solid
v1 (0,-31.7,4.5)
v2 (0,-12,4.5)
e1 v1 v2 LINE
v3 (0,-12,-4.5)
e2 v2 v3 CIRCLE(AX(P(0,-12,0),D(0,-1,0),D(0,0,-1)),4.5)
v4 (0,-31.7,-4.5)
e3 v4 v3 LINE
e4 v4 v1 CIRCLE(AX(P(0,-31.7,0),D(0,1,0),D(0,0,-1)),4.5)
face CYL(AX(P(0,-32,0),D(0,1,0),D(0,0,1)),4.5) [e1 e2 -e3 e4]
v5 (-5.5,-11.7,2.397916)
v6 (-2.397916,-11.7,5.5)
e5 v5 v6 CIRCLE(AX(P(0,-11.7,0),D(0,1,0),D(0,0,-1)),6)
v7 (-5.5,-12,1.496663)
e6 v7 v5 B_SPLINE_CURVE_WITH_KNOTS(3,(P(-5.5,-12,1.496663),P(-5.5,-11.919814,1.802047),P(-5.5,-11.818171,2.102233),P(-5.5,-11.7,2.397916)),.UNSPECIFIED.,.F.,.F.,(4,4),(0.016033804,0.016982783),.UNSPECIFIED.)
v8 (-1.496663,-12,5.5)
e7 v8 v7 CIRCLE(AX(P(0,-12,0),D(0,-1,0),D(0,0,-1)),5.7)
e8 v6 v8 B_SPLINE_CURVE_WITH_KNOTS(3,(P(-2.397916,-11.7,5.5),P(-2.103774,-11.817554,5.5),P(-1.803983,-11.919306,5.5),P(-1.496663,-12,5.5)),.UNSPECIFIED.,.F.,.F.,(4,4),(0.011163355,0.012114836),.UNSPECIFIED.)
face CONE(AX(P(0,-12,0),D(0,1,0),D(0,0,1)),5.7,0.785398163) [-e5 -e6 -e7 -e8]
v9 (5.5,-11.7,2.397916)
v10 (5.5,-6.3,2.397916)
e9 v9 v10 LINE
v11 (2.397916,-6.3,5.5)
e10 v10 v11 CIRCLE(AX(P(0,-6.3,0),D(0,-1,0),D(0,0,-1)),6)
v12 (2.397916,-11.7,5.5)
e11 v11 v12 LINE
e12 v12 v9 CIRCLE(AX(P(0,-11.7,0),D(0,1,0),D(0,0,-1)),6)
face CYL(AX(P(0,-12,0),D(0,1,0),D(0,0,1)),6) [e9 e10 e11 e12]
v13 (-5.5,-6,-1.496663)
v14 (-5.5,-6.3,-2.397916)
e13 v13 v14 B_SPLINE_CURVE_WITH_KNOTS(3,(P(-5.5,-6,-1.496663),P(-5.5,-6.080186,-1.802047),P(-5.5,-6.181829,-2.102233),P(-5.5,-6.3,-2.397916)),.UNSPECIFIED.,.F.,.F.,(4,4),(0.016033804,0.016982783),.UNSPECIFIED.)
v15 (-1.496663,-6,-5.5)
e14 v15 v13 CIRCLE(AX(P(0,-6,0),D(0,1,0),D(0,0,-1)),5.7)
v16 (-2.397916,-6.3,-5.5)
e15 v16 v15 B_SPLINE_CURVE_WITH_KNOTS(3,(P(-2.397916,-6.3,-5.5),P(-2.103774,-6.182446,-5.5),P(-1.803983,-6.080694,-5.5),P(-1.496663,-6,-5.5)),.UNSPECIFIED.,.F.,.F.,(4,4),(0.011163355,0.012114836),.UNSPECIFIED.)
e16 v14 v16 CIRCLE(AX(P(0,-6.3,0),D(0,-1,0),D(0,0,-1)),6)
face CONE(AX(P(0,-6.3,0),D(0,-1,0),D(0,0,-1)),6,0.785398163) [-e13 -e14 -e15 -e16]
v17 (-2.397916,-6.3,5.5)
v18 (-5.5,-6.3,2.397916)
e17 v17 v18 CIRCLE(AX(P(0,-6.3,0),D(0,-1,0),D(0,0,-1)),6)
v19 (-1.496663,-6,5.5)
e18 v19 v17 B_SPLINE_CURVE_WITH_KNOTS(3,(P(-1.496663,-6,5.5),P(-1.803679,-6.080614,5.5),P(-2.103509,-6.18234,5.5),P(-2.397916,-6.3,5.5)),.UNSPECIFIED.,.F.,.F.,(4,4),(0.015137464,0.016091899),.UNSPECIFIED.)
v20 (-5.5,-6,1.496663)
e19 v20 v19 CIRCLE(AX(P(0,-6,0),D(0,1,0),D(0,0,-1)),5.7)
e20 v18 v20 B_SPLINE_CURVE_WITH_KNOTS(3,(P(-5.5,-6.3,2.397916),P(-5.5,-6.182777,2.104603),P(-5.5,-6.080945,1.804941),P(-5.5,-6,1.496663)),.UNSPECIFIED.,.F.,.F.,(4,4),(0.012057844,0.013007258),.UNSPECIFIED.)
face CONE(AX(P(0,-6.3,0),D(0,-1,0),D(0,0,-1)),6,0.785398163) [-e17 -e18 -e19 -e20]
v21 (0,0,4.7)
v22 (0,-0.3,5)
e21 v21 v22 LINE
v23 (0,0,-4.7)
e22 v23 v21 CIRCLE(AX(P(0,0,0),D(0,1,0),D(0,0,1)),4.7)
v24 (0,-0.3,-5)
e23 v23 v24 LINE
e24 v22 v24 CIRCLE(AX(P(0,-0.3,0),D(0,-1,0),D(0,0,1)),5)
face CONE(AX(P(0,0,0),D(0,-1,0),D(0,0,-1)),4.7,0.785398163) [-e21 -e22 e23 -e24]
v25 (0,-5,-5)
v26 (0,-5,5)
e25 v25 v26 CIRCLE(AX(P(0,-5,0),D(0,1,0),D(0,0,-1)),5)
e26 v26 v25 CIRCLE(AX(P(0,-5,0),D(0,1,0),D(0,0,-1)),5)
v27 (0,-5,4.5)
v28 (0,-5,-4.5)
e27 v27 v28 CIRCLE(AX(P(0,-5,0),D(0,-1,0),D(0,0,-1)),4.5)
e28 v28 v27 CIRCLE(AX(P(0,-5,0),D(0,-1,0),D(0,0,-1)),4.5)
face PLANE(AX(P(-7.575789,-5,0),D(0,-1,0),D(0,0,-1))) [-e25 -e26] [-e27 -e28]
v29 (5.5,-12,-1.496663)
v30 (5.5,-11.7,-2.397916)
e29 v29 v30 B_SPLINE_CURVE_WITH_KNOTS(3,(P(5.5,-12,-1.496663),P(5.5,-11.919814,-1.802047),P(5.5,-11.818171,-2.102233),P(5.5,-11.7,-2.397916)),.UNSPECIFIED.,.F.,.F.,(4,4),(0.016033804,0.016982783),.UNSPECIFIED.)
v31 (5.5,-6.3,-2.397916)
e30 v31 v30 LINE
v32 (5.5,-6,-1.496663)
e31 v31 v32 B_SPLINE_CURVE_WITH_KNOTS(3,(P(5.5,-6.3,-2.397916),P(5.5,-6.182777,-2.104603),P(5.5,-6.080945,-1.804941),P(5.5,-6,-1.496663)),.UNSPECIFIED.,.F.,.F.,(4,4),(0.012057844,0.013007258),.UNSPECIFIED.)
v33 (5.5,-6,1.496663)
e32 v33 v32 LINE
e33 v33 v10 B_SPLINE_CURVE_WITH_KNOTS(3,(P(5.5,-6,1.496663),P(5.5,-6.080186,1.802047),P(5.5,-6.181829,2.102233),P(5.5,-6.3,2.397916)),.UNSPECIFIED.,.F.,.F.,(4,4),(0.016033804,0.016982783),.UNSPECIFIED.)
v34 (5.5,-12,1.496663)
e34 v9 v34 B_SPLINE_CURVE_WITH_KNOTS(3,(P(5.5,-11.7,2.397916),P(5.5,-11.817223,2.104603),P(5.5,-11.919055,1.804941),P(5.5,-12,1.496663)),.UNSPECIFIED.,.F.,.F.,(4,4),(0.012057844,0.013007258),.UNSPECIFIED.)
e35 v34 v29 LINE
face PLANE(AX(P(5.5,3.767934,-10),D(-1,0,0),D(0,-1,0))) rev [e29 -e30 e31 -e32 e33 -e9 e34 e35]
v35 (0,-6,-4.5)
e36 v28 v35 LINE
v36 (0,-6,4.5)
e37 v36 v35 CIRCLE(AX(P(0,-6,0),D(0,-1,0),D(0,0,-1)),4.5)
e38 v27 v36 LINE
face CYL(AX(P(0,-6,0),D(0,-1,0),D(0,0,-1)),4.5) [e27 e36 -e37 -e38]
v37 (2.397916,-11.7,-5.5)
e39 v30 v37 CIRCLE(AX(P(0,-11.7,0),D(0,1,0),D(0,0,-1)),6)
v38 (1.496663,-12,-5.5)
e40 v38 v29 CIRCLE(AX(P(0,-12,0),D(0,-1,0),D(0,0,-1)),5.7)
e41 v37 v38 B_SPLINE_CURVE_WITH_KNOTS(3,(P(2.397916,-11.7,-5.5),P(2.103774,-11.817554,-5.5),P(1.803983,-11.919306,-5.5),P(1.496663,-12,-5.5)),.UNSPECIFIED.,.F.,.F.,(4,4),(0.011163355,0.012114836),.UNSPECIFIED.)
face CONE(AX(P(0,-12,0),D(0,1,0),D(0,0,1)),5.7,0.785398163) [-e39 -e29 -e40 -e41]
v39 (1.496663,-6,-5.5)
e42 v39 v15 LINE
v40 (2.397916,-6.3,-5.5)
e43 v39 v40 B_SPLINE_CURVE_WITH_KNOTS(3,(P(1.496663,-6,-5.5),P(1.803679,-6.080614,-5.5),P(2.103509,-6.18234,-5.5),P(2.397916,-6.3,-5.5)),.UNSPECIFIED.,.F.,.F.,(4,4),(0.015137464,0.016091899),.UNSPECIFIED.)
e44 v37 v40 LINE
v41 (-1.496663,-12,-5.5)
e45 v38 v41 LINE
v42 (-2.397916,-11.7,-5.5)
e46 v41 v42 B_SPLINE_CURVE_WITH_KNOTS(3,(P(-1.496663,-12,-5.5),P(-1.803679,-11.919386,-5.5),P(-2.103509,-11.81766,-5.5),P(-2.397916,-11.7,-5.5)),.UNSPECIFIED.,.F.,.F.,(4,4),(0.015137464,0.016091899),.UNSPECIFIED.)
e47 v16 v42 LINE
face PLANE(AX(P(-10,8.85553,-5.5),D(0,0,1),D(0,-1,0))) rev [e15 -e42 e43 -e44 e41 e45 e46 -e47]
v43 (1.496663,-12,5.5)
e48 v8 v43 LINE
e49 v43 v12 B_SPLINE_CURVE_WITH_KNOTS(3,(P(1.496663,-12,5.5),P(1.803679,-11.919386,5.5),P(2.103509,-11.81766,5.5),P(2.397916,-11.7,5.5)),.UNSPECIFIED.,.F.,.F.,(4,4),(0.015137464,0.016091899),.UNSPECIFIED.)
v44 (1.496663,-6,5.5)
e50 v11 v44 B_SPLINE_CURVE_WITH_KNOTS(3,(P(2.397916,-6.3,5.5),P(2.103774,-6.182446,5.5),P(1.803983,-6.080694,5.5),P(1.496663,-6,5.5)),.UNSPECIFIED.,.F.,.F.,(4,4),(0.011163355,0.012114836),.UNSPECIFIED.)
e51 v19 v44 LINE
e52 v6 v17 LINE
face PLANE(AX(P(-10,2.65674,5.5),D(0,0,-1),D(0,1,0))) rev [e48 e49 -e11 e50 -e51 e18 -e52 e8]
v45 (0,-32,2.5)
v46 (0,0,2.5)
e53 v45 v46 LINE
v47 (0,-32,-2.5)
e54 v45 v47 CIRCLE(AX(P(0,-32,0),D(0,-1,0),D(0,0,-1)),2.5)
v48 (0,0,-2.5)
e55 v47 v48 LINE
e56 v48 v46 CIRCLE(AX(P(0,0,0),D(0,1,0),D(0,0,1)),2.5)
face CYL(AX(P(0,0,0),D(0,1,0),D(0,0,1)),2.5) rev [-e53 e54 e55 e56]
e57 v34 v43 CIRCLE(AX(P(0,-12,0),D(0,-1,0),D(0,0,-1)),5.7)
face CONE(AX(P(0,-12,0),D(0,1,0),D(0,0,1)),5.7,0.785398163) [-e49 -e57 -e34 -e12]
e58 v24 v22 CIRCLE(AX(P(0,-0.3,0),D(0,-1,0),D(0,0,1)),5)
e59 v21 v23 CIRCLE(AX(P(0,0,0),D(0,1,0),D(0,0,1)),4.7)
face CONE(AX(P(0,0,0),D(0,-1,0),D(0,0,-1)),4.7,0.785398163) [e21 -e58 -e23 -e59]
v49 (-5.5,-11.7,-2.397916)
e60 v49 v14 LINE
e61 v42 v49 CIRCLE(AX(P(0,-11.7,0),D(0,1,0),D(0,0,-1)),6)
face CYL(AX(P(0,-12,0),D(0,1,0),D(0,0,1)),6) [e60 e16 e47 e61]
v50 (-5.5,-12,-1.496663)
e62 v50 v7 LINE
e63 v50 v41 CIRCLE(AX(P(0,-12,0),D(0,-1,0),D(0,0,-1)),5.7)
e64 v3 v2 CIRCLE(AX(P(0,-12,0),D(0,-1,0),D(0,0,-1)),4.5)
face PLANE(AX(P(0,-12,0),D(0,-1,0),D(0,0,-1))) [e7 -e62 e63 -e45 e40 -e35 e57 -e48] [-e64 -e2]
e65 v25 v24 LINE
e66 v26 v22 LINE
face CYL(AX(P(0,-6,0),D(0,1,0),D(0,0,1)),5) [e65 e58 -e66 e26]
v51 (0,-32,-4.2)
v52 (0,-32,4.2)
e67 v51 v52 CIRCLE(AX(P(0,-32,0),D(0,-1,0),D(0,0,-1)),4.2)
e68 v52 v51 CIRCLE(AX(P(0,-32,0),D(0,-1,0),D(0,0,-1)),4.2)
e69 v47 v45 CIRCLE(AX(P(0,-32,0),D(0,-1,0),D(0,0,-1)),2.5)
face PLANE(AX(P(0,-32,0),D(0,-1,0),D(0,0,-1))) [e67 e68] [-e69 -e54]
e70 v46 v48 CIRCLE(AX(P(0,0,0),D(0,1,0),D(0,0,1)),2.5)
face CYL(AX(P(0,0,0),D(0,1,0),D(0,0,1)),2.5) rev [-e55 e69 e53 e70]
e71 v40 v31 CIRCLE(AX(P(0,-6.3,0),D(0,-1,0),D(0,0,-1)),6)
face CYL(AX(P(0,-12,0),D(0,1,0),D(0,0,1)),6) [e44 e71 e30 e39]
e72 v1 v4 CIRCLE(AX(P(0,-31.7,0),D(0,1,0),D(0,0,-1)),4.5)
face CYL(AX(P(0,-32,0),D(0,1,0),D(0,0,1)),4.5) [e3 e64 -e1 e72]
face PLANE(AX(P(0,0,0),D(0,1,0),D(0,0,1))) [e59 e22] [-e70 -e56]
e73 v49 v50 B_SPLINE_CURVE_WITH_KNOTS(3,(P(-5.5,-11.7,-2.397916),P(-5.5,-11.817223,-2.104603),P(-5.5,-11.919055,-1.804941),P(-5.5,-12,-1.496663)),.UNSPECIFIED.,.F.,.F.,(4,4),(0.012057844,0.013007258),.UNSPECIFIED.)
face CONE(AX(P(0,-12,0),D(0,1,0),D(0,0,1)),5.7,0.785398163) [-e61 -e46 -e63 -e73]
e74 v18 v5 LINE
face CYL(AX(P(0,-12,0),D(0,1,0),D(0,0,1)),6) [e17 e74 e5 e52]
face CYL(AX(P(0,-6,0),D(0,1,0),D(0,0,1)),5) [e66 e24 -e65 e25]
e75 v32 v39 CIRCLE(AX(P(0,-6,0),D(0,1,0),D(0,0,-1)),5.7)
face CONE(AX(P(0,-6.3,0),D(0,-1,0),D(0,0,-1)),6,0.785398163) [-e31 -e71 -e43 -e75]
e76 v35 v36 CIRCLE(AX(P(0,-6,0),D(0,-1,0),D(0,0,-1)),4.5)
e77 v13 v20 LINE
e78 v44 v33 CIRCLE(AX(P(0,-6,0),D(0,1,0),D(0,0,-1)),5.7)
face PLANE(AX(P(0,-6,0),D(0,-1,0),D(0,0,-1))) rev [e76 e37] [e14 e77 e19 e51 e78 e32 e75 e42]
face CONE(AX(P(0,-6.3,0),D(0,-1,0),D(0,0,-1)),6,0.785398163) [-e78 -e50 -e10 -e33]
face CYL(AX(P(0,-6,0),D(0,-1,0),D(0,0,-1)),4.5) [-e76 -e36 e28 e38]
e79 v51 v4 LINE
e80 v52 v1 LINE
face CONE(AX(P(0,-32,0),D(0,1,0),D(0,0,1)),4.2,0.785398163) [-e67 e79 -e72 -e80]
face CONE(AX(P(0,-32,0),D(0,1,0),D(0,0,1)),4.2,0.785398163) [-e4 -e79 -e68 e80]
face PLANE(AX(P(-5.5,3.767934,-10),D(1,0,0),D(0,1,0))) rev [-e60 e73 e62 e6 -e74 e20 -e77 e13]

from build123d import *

# Parameters (mm, degrees)
SKETCH_1_R            = 5
EXTRUDE_1_DEPTH       = 6
SKETCH_2_R            = 6
EXTRUDE_2_DEPTH       = 6
SKETCH_3_R            = 4.5
EXTRUDE_3_DEPTH       = 20
CHAMFER_1_SIZE        = 0.3
SKETCH_7_W            = 8.670570122
SKETCH_7_H            = 17.253558728
SKETCH_7_W_2          = 11.735923196
CUT_EXTRUDE_1_DEPTH   = 10
HOLE_WIZARD_5_0_5_1_D = 5
SKETCH_8_W            = 3.075789072
SKETCH_8_H            = 1
SKETCH_9_W            = 7.38579235
SKETCH_9_H            = 17.49729378
SKETCH_9_W_2          = 12.485506115
SKETCH_9_H_2          = 24.97101223
CUT_EXTRUDE_2_DEPTH   = 10
CHAMFER_7_SIZE        = 0.3


with BuildPart() as part:
    # 草图1 → 凸台-拉伸1 (new body)
    with BuildSketch(Plane(origin=(0, 0, 0), x_dir=(1, 0, 0), z_dir=(0, 1, 0))):
        with Locations(Location((0, 0, 0), (0, 0, 270))):
            Circle(SKETCH_1_R)
    extrude(amount=-EXTRUDE_1_DEPTH)

    # 草图2 → 凸台-拉伸2 (add)
    with BuildSketch(Plane.XZ.offset(6)):
        with Locations(Location((0, 0, 0), (0, 0, 270))):
            Circle(SKETCH_2_R)
    extrude(amount=EXTRUDE_2_DEPTH)

    # 草图3 → 凸台-拉伸3 (add)
    with BuildSketch(Plane.XZ.offset(12)):
        with Locations(Location((0, 0, 0), (0, 0, 270))):
            Circle(SKETCH_3_R)
    extrude(amount=EXTRUDE_3_DEPTH)

    # 倒角1
    chamfer_1_edges = [part.edges().sort_by_distance(p)[0] for p in [
        (0, 0, -5),
        (0, -6, 6),
        (0, -12, 6),
    ]]
    chamfer(chamfer_1_edges, length=CHAMFER_1_SIZE)

    # 草图7 → 切除-拉伸1 (cut, symmetric)
    with BuildSketch(Plane.XY):
        with Locations((-9.835285061, -4.858845759)):
            Rectangle(SKETCH_7_W, SKETCH_7_H)
        with Locations((11.367961598, -4.858845759)):
            Rectangle(SKETCH_7_W_2, SKETCH_7_H)
    extrude(amount=CUT_EXTRUDE_1_DEPTH, both=True, mode=Mode.SUBTRACT)

    # Ø5.0 (5) 直径孔1 (through all)
    with Locations(Plane(origin=(0, 0, 0), x_dir=(1, 0, 0), z_dir=(0, 1, 0))):
        with Locations((0, 0)):
            Hole(HOLE_WIZARD_5_0_5_1_D / 2)

    # 草图8 → 切除-旋转1 (revolve, cut)
    with BuildSketch(Plane.XY, mode=Mode.PRIVATE) as cut_revolve_1_sk:
        with Locations((-6.037894536, -5.5)):
            Rectangle(SKETCH_8_W, SKETCH_8_H)
    revolve(cut_revolve_1_sk.sketch.rotate(Axis((0, -6, 0), (0, 1, 0)), 270), axis=Axis((0, -6, 0), (0, 1, 0)), mode=Mode.SUBTRACT)

    # 草图9 → 切除-拉伸2 (cut, symmetric)
    with BuildSketch(Plane(origin=(0, 0, 0), x_dir=(0, 0, -1), z_dir=(1, 0, 0))):
        with Locations((-9.192896175, -6.091907364)):
            Rectangle(SKETCH_9_W, SKETCH_9_H)
        with Locations((11.742753057, -3.629976581)):
            Rectangle(SKETCH_9_W_2, SKETCH_9_H_2)
    extrude(amount=CUT_EXTRUDE_2_DEPTH, both=True, mode=Mode.SUBTRACT)

    # 倒角7
    chamfer_7_edges = [part.edges().sort_by_distance(p)[0] for p in [
        (0, -32, 4.5),
    ]]
    chamfer(chamfer_7_edges, length=CHAMFER_7_SIZE)


solid = part.part
